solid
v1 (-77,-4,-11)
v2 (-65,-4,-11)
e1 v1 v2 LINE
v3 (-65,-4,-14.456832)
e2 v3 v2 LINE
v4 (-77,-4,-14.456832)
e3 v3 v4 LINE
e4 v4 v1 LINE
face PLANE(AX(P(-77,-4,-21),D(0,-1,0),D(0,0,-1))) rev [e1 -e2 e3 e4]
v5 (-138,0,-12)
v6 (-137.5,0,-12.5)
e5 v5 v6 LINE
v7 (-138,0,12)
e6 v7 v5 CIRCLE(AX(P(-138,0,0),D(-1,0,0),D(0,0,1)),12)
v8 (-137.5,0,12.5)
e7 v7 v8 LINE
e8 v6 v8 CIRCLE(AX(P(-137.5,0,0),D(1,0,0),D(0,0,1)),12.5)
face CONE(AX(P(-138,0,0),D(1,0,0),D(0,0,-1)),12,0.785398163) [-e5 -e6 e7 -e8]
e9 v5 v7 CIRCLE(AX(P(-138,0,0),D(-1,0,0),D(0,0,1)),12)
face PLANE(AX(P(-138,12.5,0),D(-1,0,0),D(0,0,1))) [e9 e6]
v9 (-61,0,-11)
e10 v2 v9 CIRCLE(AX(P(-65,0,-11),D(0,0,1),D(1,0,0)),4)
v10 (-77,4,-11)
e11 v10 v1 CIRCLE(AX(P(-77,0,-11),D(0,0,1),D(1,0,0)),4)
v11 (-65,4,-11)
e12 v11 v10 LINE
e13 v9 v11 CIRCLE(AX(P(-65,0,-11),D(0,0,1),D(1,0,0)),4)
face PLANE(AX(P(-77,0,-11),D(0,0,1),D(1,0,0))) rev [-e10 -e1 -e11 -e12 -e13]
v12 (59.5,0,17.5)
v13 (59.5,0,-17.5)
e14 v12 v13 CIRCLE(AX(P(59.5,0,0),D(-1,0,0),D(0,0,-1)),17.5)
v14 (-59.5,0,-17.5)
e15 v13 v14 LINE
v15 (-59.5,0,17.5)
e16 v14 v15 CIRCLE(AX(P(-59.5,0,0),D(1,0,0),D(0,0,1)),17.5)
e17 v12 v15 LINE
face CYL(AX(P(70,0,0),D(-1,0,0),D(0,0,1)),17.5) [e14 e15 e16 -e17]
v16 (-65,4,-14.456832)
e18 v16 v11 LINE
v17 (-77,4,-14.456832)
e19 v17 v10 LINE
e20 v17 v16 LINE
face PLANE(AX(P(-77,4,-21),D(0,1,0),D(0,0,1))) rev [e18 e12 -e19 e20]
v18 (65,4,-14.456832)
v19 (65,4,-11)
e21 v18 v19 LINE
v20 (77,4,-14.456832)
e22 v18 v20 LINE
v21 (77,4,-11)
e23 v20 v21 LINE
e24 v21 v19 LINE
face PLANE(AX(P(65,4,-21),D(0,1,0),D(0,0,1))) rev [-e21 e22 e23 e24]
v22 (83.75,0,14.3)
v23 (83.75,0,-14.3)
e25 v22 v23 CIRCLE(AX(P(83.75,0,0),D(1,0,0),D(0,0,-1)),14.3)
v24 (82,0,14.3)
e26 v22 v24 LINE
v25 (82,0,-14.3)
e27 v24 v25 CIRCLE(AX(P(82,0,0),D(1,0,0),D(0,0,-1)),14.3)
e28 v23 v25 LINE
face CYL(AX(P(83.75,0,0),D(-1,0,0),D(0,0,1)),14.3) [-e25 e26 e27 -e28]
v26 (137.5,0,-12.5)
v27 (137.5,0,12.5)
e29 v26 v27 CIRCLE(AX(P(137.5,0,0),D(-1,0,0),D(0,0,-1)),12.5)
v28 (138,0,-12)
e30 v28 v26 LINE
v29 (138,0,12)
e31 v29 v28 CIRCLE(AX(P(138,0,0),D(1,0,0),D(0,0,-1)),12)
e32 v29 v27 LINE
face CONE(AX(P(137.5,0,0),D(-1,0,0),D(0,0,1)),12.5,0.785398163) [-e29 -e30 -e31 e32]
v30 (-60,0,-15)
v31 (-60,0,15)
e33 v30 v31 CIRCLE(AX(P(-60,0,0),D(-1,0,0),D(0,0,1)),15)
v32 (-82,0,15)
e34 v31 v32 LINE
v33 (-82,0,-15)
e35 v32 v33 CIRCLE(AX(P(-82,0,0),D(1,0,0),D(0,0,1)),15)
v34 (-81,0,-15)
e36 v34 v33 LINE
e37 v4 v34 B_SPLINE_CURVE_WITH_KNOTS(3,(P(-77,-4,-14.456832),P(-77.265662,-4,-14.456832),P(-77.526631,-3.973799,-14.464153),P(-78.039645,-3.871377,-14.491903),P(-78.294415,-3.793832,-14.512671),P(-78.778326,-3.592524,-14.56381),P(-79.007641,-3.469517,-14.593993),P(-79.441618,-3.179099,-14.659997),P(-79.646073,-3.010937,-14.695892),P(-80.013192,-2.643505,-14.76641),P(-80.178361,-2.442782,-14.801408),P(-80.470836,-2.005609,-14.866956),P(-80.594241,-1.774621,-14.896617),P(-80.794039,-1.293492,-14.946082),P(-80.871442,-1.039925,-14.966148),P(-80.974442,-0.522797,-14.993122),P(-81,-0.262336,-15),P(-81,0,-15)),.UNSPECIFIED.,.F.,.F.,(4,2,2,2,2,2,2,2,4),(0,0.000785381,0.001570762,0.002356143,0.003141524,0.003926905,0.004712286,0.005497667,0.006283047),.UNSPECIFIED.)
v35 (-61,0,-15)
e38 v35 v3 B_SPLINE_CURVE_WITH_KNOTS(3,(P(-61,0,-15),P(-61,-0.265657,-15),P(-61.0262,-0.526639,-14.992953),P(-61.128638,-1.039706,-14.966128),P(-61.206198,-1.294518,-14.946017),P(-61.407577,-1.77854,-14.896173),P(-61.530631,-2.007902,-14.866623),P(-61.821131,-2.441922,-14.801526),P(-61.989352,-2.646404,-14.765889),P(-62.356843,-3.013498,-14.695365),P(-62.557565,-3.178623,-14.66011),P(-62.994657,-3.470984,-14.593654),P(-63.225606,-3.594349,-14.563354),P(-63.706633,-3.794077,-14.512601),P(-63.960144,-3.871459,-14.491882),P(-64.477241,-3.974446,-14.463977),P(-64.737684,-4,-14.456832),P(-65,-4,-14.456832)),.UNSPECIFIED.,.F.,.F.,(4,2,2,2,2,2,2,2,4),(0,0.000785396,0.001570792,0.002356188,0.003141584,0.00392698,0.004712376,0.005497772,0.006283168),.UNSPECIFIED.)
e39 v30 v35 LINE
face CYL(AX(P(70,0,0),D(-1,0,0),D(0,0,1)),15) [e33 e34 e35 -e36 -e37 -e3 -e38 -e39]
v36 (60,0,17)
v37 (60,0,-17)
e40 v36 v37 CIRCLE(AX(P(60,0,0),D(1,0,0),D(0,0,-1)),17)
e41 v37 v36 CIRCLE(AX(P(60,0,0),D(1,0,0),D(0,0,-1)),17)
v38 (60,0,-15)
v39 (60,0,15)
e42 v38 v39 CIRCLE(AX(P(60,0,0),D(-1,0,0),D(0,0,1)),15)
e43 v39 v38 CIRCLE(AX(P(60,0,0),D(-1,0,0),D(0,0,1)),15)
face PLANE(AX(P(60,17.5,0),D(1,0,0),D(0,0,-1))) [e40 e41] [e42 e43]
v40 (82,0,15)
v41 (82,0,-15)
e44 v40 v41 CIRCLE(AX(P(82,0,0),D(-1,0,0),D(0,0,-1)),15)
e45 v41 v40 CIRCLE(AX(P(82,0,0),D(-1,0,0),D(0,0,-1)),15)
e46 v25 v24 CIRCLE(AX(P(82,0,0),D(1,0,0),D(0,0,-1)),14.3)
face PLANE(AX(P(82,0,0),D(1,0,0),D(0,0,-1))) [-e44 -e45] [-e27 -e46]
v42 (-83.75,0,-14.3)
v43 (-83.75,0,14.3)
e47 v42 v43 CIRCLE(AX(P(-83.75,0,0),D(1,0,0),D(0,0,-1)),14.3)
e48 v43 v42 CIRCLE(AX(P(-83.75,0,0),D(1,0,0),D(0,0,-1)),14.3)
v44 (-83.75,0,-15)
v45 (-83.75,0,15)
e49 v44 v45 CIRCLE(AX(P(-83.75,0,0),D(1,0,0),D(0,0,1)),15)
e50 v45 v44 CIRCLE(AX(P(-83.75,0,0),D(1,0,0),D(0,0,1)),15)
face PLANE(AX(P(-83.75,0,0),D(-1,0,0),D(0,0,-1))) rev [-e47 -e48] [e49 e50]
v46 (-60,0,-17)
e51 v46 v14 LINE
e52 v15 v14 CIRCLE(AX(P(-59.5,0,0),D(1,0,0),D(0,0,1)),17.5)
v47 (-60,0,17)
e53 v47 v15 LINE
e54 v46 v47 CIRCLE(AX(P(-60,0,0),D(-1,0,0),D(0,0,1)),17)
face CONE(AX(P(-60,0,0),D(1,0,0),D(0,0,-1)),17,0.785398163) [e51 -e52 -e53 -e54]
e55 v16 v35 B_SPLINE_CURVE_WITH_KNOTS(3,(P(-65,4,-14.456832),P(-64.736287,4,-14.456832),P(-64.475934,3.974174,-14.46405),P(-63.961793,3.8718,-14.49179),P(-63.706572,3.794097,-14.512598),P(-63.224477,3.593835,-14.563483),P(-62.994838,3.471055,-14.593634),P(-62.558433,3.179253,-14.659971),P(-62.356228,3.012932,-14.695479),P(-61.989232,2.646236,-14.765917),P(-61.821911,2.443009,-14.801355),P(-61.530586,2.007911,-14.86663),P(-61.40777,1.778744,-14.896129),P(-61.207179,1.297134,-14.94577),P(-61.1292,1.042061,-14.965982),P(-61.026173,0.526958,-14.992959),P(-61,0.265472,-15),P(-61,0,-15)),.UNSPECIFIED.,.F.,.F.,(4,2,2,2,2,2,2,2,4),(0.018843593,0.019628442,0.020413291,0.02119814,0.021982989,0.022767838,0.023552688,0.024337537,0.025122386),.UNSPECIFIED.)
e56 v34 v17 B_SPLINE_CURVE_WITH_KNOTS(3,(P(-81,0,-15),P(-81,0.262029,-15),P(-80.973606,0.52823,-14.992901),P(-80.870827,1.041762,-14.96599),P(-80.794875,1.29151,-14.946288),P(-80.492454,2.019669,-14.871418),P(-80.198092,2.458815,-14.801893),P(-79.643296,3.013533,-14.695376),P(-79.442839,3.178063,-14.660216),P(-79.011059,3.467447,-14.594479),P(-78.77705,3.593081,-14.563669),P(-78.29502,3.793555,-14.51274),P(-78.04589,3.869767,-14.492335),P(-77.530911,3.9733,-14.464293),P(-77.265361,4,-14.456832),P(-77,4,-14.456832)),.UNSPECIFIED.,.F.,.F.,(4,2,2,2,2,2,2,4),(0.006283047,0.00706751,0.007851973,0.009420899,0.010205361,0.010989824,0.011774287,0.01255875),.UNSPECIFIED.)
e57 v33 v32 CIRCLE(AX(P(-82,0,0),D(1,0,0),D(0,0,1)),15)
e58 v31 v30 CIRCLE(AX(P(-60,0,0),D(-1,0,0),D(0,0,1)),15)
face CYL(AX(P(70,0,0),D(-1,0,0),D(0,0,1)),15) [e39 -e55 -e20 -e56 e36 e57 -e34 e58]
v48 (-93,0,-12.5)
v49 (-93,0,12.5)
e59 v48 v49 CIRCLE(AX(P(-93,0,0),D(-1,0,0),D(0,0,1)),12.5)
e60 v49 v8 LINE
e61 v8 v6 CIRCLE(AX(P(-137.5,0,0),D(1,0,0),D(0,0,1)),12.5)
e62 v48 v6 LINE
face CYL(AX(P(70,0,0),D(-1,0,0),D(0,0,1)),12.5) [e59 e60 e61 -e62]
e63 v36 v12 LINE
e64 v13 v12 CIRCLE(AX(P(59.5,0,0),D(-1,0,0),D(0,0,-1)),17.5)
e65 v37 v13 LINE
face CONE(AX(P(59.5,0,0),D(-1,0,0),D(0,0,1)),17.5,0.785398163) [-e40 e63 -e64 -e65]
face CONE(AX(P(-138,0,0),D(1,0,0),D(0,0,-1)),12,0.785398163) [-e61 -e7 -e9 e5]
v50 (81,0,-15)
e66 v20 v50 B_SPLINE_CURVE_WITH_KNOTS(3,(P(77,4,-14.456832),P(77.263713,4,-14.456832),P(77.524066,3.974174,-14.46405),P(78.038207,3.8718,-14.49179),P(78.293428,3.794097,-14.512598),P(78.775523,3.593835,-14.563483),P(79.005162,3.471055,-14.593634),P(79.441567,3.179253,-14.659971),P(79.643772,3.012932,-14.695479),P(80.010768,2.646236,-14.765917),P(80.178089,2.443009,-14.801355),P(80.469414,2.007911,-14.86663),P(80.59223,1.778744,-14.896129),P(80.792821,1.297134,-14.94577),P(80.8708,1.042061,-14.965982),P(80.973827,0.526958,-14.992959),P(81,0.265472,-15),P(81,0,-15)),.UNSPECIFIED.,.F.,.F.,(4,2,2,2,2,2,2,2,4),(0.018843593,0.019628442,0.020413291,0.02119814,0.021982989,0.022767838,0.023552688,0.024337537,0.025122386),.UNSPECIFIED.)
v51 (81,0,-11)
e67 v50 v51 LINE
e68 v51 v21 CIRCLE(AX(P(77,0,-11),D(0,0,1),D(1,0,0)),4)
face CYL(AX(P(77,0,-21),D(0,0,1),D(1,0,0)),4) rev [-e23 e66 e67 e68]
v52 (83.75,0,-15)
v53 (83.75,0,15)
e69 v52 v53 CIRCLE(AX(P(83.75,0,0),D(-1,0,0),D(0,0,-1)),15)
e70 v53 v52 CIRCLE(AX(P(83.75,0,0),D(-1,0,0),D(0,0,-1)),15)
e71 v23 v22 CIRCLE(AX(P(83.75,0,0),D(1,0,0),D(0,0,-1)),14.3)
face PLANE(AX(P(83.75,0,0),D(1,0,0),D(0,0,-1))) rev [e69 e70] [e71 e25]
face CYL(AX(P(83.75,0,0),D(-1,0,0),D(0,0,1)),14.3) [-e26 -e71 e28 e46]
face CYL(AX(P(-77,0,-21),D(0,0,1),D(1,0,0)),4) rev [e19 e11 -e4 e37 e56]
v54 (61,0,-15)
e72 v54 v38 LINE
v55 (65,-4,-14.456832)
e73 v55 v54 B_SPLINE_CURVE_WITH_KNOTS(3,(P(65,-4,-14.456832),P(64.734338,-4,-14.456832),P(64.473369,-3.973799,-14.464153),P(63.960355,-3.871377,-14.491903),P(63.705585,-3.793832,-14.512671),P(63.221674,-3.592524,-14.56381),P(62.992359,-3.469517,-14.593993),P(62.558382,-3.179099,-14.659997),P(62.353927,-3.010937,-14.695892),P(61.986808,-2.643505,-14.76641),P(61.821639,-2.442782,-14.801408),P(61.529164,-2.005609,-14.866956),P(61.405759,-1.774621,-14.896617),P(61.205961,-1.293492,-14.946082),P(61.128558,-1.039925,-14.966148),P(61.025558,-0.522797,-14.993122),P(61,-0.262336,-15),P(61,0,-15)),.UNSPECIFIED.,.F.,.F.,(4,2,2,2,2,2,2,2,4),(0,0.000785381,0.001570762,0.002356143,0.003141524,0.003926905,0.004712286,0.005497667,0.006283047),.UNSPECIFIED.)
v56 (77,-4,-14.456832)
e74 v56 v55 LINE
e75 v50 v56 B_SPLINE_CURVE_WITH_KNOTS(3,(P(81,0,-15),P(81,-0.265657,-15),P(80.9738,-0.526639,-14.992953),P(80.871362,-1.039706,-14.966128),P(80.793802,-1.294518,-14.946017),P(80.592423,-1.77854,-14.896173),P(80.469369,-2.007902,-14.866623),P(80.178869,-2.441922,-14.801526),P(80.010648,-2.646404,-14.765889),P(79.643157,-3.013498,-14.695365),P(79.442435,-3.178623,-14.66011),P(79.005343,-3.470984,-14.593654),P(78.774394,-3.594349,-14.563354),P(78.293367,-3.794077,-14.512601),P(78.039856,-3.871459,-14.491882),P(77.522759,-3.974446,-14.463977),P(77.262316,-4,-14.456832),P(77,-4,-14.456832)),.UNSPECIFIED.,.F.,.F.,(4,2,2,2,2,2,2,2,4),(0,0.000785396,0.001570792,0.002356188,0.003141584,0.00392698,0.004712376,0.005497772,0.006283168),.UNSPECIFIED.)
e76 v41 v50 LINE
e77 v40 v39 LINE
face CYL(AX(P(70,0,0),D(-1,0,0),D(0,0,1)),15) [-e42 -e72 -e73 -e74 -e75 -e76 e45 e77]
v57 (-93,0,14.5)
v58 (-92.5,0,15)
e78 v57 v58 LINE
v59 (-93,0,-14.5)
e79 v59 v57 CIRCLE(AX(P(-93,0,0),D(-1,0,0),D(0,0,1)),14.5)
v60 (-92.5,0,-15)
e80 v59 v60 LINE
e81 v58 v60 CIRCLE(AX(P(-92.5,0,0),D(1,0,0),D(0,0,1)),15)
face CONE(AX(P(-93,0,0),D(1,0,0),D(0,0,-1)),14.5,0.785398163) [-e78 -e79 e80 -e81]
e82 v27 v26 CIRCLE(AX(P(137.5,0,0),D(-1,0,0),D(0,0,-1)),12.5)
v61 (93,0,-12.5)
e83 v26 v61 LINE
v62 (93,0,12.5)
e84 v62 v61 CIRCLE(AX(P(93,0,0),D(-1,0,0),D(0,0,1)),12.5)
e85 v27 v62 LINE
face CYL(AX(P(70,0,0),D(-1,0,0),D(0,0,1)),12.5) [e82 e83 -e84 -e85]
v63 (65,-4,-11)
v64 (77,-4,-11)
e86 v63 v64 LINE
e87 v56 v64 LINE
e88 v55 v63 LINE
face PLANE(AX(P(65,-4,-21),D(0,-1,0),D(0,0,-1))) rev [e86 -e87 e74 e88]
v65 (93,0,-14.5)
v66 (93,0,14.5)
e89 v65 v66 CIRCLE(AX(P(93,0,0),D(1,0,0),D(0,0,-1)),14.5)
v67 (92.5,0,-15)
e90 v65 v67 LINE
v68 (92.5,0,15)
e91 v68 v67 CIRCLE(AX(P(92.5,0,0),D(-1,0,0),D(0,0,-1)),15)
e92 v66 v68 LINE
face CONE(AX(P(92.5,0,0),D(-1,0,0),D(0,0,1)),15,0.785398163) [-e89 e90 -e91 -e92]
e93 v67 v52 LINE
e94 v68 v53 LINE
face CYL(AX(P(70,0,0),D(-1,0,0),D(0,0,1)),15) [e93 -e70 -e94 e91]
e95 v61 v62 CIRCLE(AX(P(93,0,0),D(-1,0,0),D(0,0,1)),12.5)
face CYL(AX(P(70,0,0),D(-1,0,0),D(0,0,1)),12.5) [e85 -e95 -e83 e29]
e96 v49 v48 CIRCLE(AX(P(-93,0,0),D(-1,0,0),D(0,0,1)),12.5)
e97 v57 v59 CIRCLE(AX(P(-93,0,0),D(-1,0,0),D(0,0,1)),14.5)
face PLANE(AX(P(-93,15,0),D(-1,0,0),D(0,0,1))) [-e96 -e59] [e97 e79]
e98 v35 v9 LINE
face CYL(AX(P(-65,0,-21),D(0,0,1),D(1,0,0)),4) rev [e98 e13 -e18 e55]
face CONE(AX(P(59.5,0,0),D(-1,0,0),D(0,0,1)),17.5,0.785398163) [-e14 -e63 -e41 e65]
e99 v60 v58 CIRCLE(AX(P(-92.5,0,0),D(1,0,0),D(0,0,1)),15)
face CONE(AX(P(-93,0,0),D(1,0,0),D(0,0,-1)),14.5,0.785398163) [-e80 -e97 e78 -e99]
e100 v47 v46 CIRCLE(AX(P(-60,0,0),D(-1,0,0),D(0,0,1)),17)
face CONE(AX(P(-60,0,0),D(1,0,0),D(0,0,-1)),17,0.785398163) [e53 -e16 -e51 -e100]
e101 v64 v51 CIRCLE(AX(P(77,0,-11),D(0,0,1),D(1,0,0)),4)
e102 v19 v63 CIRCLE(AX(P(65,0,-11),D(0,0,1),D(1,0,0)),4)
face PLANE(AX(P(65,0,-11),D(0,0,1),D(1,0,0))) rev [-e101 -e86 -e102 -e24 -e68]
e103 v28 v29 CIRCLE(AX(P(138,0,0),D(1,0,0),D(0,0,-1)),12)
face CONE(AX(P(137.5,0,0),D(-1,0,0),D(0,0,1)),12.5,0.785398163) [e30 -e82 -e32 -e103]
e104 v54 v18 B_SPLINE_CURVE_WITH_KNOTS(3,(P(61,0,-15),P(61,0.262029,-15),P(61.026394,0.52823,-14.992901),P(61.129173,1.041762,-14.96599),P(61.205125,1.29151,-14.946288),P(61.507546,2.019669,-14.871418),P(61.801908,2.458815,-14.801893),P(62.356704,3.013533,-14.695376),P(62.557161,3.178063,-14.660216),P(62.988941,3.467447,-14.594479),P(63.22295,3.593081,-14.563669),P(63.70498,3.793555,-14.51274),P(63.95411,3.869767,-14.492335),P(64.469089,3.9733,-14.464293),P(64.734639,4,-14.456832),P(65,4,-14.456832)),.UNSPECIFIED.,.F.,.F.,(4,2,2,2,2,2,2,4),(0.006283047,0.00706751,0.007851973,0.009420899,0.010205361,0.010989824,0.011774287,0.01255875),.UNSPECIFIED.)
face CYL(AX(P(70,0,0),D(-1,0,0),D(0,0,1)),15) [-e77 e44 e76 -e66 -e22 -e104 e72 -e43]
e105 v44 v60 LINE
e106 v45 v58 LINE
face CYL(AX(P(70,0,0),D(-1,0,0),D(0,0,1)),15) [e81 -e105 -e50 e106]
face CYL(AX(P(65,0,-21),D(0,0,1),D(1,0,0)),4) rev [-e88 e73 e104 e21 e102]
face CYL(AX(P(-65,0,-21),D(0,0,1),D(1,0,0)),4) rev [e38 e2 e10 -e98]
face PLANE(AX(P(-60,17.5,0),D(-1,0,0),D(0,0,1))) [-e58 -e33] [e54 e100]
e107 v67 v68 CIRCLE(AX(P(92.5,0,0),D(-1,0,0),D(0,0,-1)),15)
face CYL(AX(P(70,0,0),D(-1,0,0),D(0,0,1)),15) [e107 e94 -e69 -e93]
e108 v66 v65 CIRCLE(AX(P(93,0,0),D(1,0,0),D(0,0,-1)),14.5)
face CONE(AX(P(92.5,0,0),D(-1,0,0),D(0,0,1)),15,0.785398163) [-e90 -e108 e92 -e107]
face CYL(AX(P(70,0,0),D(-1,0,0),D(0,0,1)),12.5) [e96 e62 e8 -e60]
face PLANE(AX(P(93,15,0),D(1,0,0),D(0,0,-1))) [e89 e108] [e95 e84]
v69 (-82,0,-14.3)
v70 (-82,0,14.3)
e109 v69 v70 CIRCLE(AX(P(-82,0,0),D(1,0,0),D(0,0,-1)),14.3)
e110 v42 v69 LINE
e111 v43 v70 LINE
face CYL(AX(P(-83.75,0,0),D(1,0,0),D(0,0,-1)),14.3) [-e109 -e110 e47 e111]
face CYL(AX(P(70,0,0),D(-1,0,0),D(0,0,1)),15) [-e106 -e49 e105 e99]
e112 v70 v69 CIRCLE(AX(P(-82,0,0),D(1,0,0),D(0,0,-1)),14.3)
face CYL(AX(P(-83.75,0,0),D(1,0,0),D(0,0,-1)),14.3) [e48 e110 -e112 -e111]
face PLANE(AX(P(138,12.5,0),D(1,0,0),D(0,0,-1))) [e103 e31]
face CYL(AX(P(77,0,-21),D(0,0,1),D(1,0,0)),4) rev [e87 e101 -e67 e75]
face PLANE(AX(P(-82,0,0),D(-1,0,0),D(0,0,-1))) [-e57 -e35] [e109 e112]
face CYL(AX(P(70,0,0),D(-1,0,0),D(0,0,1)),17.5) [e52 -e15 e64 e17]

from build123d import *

# Parameters (mm, degrees)
CHAMFER_1_SIZE      = 0.5
CUT_EXTRUDE_START   = -11
CUT_EXTRUDE_1_DEPTH = 10
SKETCH_11_R         = 20.368798622
SKETCH_11_R_2       = 14.3
CUT_EXTRUDE_3_DEPTH = 1.75
CHAMFER_3_SIZE      = 0.5


with BuildPart() as part:
    # 草图1 → 旋转1 (revolve)
    with BuildSketch(Plane(origin=(0, 0, 0), x_dir=(-1, 0, 0), z_dir=(0, 0, -1)), mode=Mode.PRIVATE) as revolve_1_sk:
        Polygon((-60, 17.5), (60, 17.5), (60, 15), (93, 15), (93, 12.5), (138, 12.5), (138, 0), (-138, 0), (-138, 12.5), (-93, 12.5), (-93, 15), (-60, 15), align=None)
    revolve(revolve_1_sk.sketch.rotate(Axis((70, 0, 0), (-1, 0, 0)), 270), axis=Axis((70, 0, 0), (-1, 0, 0)))

    # 倒角1
    chamfer_1_edges = [part.edges().sort_by_distance(p)[0] for p in [
        (-138, 0, -12.5),
        (-93, 0, -15),
        (-60, 0, -17.5),
        (60, 0, -17.5),
        (93, 0, -15),
    ]]
    chamfer(chamfer_1_edges, length=CHAMFER_1_SIZE)

    # 草图2 → 切除-拉伸1 (cut)
    with BuildSketch(Plane.XY.offset(CUT_EXTRUDE_START)):
        with BuildLine():
            Line((-77, 4), (-65, 4))
            ThreePointArc((-65, 4), (-61, 0), (-65, -4))
            Line((-65, -4), (-77, -4))
            ThreePointArc((-77, -4), (-81, 0), (-77, 4))
        make_face()
        with BuildLine():
            Line((65, 4), (77, 4))
            ThreePointArc((77, 4), (81, 0), (77, -4))
            Line((77, -4), (65, -4))
            ThreePointArc((65, -4), (61, 0), (65, 4))
        make_face()
    extrude(amount=-CUT_EXTRUDE_1_DEPTH, mode=Mode.SUBTRACT)

    # 草图11 → 切除-拉伸3 (cut)
    with BuildSketch(Plane(origin=(82, 0, 0), x_dir=(0, 0, -1), z_dir=(1, 0, 0))):
        Circle(SKETCH_11_R)
        Circle(SKETCH_11_R_2, mode=Mode.SUBTRACT)
    cut_extrude_3 = extrude(amount=CUT_EXTRUDE_3_DEPTH, mode=Mode.SUBTRACT)

    # 镜向1: 切除-拉伸3 across plane
    add(cut_extrude_3.mirror(Plane(origin=(0, 0, 0), x_dir=(0, 0, 1), z_dir=(1, 0, 0))), mode=Mode.SUBTRACT)

    # 倒角3
    chamfer_3_edges = [part.edges().sort_by_distance(p)[0] for p in [
        (138, 0, -12.5),
    ]]
    chamfer(chamfer_3_edges, length=CHAMFER_3_SIZE)


solid = part.part
